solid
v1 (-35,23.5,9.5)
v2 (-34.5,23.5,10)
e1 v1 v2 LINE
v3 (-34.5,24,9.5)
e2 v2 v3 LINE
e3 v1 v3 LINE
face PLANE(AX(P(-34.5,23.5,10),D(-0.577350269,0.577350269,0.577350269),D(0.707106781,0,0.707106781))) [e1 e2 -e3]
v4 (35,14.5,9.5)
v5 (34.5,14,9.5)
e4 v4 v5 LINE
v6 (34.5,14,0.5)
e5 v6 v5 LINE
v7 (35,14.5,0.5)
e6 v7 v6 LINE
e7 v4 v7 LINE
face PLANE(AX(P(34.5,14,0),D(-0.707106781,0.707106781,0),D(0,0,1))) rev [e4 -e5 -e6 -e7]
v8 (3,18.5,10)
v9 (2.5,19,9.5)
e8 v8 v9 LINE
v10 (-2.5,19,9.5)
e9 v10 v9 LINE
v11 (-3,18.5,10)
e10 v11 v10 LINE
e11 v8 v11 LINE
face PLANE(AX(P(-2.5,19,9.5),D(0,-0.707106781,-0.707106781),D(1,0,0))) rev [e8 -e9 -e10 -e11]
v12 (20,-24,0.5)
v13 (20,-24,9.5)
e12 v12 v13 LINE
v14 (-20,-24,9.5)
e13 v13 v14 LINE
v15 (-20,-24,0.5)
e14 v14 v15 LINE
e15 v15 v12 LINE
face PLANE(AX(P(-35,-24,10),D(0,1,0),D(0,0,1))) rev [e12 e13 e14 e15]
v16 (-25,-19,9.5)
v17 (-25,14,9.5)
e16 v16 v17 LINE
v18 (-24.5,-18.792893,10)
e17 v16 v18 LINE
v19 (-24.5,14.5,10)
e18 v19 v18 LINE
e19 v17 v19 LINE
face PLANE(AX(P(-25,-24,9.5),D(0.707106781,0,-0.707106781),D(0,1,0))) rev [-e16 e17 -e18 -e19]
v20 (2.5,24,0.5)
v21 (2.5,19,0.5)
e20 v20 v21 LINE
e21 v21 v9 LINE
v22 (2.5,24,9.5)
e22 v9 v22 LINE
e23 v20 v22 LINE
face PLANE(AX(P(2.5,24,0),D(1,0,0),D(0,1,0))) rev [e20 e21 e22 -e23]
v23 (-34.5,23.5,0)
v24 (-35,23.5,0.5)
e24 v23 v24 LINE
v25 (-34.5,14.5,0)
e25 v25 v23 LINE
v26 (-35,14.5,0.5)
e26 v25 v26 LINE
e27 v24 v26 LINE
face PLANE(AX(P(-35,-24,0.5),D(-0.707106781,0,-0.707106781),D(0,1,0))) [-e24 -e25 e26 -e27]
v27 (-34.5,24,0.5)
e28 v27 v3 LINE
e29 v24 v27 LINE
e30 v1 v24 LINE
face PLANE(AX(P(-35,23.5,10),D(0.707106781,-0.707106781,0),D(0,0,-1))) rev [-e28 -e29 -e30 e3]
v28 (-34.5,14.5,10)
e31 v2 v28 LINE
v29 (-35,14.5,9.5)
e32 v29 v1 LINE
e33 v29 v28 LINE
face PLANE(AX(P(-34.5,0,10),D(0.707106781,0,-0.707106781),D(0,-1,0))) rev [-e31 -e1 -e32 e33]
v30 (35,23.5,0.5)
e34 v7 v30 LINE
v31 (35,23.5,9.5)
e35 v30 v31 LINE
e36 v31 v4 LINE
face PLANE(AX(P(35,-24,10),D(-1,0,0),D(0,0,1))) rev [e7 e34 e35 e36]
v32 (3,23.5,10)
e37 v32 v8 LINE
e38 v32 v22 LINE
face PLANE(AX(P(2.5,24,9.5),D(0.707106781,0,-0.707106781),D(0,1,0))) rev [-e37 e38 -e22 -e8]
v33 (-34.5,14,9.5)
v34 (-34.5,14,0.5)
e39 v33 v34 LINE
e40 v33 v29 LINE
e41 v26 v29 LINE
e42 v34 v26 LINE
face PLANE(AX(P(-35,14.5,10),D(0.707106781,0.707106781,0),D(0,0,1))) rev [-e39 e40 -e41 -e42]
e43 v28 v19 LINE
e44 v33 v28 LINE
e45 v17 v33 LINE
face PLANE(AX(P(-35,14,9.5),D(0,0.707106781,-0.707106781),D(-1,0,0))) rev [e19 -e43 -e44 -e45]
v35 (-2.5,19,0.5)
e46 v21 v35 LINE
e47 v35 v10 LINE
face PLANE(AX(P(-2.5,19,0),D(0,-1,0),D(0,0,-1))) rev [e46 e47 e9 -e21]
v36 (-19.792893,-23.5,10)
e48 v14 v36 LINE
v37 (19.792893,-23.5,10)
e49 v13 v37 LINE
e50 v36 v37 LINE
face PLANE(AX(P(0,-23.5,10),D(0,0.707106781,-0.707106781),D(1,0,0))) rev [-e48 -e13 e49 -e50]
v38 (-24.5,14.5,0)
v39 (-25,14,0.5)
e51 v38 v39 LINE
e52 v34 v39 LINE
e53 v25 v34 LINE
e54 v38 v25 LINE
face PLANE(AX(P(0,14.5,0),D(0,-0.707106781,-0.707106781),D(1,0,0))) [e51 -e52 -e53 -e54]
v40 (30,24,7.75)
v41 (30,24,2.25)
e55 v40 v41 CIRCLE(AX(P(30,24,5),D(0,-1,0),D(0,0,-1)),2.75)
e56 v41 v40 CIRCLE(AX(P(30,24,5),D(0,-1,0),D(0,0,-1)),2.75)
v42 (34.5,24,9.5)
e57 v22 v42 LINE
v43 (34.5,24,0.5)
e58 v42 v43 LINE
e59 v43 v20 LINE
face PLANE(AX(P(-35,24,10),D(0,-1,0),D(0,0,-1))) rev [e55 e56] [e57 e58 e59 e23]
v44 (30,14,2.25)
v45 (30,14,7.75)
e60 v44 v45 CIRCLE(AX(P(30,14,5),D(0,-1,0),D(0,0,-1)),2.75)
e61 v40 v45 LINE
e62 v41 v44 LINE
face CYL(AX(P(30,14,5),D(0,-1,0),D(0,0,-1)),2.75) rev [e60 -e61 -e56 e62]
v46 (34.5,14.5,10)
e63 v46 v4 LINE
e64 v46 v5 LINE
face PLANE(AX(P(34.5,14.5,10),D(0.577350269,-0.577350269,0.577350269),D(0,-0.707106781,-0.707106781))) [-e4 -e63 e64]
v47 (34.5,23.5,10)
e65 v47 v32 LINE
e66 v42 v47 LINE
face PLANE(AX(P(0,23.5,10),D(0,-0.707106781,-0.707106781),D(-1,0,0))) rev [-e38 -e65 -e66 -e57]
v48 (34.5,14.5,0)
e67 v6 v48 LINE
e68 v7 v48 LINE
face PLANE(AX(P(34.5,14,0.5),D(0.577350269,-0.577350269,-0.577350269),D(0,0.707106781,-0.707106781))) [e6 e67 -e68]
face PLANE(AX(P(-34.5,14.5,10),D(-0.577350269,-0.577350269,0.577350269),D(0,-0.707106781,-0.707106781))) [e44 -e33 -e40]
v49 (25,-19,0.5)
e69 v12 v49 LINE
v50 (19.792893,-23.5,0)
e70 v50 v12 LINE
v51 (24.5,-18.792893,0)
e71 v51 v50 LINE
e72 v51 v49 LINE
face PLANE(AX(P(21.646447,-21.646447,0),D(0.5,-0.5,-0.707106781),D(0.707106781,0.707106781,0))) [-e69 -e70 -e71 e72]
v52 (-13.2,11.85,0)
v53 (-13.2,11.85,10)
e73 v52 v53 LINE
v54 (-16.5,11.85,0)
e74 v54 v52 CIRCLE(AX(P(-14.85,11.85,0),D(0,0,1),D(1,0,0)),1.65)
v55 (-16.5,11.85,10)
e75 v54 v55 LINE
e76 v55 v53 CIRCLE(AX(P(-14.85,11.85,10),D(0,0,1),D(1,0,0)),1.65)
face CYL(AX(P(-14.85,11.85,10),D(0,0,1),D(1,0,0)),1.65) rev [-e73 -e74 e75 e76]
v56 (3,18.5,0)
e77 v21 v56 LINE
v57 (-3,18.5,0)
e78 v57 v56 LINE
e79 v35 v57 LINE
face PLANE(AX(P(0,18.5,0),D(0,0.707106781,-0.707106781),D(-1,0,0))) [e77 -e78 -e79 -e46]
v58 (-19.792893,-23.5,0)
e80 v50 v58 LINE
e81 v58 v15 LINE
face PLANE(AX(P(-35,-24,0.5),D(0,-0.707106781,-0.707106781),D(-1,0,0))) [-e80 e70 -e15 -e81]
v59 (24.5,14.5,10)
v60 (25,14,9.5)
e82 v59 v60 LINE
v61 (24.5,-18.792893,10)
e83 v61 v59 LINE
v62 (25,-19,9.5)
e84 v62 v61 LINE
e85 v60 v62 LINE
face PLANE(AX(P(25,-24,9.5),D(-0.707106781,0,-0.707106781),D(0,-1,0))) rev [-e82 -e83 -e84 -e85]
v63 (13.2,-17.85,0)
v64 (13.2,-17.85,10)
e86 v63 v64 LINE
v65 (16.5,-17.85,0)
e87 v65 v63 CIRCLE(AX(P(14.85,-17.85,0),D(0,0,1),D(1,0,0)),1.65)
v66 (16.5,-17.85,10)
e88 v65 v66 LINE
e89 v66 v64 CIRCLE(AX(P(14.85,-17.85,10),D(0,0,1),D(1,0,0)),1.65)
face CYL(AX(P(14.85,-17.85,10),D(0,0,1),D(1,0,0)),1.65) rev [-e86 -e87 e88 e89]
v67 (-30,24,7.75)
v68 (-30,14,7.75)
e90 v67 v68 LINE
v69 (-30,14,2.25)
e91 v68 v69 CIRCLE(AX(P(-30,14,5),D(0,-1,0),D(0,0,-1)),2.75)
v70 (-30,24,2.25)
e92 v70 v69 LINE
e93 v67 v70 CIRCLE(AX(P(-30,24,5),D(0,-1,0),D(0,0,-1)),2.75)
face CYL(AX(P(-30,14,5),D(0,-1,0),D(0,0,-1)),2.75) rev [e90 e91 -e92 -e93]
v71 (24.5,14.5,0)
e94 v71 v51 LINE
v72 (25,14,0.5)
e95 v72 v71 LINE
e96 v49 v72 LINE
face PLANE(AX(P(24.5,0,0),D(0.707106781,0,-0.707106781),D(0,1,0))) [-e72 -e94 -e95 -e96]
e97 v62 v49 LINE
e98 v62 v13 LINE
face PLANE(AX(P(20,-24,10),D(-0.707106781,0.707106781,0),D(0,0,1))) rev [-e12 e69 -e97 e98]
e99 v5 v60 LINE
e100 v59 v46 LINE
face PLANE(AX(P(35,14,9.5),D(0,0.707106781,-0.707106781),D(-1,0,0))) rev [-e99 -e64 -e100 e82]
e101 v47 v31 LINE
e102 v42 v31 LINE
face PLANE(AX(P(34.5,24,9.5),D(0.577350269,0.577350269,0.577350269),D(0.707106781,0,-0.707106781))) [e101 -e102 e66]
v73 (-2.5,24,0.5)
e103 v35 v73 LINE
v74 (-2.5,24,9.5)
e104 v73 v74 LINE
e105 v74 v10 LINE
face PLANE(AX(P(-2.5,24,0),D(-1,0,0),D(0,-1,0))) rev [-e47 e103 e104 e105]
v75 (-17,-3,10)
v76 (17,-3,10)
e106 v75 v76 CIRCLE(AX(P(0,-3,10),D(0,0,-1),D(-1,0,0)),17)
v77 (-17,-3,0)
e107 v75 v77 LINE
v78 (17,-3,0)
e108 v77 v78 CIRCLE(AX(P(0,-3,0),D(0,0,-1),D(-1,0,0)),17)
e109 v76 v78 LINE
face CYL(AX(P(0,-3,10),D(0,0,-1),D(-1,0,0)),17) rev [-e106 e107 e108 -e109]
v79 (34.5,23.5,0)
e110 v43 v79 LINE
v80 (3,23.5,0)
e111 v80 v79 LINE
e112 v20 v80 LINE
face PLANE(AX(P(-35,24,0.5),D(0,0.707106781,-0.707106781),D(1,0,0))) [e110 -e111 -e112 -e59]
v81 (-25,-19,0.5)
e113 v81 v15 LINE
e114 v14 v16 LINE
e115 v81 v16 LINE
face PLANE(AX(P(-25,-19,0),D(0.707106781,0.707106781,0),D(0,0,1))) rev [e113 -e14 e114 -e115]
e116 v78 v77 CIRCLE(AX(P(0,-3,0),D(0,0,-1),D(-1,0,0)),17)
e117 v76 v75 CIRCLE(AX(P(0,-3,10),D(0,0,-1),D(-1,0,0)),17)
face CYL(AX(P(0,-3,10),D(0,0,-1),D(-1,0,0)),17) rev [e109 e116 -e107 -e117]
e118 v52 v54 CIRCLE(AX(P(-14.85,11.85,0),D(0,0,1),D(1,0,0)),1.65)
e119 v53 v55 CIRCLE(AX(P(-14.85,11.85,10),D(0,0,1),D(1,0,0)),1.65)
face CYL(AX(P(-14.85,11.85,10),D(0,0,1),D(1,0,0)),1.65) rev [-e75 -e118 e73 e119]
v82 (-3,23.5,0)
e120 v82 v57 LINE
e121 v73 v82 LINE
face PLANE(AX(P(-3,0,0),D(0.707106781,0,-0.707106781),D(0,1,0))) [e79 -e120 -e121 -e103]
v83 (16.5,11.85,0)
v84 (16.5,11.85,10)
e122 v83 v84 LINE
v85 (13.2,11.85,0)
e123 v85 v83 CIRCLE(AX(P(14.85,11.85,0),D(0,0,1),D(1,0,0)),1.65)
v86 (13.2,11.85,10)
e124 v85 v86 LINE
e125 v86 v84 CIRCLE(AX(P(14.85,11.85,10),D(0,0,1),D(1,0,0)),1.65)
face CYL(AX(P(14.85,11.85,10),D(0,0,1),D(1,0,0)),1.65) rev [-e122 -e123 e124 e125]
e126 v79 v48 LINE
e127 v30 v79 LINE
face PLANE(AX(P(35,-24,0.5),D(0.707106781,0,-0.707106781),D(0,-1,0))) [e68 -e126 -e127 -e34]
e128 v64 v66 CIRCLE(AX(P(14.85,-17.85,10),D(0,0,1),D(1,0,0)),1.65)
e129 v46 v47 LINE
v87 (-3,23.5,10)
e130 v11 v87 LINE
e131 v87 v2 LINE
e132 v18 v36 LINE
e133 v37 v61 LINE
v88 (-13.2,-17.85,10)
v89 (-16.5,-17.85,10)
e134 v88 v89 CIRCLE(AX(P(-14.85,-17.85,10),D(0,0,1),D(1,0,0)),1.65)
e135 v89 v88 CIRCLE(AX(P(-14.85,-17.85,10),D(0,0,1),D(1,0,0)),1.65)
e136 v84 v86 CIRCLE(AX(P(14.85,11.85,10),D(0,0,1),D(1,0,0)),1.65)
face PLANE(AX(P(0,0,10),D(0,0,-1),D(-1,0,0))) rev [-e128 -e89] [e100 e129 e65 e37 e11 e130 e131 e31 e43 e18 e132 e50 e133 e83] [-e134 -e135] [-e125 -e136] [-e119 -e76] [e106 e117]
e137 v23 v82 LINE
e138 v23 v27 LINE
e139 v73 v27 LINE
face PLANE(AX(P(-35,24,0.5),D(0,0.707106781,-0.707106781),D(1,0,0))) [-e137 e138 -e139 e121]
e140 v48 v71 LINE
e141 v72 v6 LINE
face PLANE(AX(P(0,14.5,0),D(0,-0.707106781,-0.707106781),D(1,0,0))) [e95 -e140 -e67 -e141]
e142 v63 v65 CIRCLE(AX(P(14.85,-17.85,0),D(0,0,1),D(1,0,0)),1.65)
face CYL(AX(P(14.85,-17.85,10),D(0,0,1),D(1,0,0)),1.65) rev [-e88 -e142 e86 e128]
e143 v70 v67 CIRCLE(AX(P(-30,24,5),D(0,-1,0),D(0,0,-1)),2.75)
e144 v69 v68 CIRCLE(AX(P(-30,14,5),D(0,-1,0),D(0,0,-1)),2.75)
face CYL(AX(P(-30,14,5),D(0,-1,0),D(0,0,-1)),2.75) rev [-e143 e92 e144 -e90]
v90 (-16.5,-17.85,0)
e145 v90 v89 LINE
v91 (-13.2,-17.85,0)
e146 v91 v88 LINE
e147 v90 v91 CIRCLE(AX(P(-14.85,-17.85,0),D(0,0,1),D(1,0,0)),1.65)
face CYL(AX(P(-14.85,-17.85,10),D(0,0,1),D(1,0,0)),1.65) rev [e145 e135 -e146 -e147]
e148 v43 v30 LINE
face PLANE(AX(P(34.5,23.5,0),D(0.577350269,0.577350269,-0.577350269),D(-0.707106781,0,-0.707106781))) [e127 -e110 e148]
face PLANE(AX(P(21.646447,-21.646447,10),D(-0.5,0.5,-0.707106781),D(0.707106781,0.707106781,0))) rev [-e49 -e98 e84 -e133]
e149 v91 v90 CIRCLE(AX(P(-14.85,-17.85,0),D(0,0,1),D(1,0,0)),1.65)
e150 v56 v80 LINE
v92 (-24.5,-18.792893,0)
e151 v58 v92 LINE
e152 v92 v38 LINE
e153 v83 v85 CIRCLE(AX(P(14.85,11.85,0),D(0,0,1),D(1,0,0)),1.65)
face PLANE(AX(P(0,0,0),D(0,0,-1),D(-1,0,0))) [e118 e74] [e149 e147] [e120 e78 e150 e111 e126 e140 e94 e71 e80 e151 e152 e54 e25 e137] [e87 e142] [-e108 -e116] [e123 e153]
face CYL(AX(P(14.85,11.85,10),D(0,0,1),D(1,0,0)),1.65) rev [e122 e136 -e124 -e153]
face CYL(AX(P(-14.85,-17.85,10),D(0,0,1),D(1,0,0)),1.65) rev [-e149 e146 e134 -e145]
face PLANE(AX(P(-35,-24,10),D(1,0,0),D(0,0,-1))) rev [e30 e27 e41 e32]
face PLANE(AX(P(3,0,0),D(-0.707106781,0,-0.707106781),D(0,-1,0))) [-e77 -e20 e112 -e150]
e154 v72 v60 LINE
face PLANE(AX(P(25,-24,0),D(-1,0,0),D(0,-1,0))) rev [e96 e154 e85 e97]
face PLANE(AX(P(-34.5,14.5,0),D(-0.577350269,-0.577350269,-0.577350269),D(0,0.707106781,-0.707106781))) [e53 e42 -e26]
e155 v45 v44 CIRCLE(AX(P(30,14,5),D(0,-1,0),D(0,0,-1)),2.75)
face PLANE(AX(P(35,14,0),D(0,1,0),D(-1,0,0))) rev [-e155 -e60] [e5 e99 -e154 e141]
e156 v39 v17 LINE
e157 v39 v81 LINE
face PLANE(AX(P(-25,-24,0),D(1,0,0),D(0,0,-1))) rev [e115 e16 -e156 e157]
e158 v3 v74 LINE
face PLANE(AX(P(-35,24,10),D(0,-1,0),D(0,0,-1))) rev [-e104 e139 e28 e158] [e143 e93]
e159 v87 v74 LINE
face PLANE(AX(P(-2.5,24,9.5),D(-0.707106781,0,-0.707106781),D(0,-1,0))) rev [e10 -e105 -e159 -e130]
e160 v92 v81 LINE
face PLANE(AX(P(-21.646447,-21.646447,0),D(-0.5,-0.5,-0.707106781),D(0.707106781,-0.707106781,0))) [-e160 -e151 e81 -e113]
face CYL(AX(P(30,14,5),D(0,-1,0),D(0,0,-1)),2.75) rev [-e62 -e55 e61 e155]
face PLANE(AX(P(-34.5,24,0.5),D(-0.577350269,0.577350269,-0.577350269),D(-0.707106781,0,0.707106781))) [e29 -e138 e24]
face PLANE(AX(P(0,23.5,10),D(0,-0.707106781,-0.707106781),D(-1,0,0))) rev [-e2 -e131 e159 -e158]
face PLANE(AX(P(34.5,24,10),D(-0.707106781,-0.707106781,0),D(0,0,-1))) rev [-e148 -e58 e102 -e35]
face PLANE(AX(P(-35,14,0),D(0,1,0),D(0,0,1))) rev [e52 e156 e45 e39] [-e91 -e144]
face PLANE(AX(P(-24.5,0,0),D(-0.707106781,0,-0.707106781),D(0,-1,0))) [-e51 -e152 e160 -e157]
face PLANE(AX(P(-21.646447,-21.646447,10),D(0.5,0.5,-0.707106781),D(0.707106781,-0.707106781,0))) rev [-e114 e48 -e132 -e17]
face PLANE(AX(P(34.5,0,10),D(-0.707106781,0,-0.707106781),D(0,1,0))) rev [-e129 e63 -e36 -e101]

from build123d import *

# Parameters (mm, degrees)
SKETCH_1_W              = 70
SKETCH_1_H              = 48
EXTRUDE_1_DEPTH         = 10
SKETCH_2_W              = 10
SKETCH_2_H              = 38
CUT_EXTRUDE_1_DEPTH     = 44.600458713
SKETCH_3_R              = 17
CUT_EXTRUDE_2_DEPTH     = 44.600458713
HOLE_WIZARD_M4_2_D      = 3.3
HOLE_WIZARD_5_5_5_5_1_D = 5.5
CHAMFER_1_SIZE          = 5
SKETCH_12_W             = 5
SKETCH_12_H             = 5
CUT_EXTRUDE_3_DEPTH     = 44.600458713
CHAMFER_2_SIZE          = 0.5


with BuildPart() as part:
    # 草图1 → 凸台-拉伸1 (new body)
    with BuildSketch(Plane.XY):
        Rectangle(SKETCH_1_W, SKETCH_1_H)
    extrude(amount=EXTRUDE_1_DEPTH)

    # 草图2 → 切除-拉伸1 (cut, through all)
    with BuildSketch(Plane.XY.offset(10)):
        with Locations((-30, -5)):
            Rectangle(SKETCH_2_W, SKETCH_2_H)
        with Locations((30, -5)):
            Rectangle(SKETCH_2_W, SKETCH_2_H)
    extrude(amount=-CUT_EXTRUDE_1_DEPTH, mode=Mode.SUBTRACT)

    # 草图3 → 切除-拉伸2 (cut, through all)
    with BuildSketch(Plane(origin=(0, 0, 0), x_dir=(-1, 0, 0), z_dir=(0, 0, -1))):
        with Locations((0, -3)):
            Circle(SKETCH_3_R)
    extrude(amount=-CUT_EXTRUDE_2_DEPTH, mode=Mode.SUBTRACT)

    # M4 螺纹孔2 (through all)
    with Locations(Plane.XY.offset(10)):
        with Locations((14.85, -17.85), (-14.85, -17.85), (-14.85, 11.85), (14.85, 11.85)):
            Hole(HOLE_WIZARD_M4_2_D / 2)

    # Ø5.5 (5.5) 直径孔1 (through all)
    with Locations(Plane(origin=(0, 14, 0), x_dir=(-1, 0, 0), z_dir=(0, -1, 0))):
        with Locations((-30, -5), (30, -5)):
            Hole(HOLE_WIZARD_5_5_5_5_1_D / 2)

    # 倒角1
    chamfer_1_edges = [part.edges().sort_by_distance(p)[0] for p in [
        (-25, -24, 5),
        (25, -24, 5),
    ]]
    chamfer(chamfer_1_edges, length=CHAMFER_1_SIZE)

    # 草图12 → 切除-拉伸3 (cut, through all)
    with BuildSketch(Plane.XY.offset(10)):
        with Locations((0, 21.5)):
            Rectangle(SKETCH_12_W, SKETCH_12_H)
    extrude(amount=-CUT_EXTRUDE_3_DEPTH, mode=Mode.SUBTRACT)

    # 倒角2
    chamfer_2_edges = [part.edges().sort_by_distance(p)[0] for p in [
        (-35, 19, 10),
        (-30, 14, 0),
        (-35, 14, 5),
        (-30, 14, 10),
        (35, 19, 0),
        (35, 19, 10),
        (25, -2.5, 0),
        (30, 14, 0),
        (35, 14, 5),
        (30, 14, 10),
        (25, -2.5, 10),
        (-35, 19, 0),
        (18.75, 24, 0),
        (18.75, 24, 10),
        (-35, 24, 5),
        (35, 24, 5),
        (-25, -2.5, 10),
        (-25, -2.5, 0),
        (0, -24, 10),
        (22.5, -21.5, 10),
        (-22.5, -21.5, 10),
        (0, -24, 0),
        (22.5, -21.5, 0),
        (-22.5, -21.5, 0),
        (-18.75, 24, 0),
        (-18.75, 24, 10),
        (-2.5, 21.5, 0),
        (2.5, 21.5, 0),
        (0, 19, 0),
        (-2.5, 21.5, 10),
        (0, 19, 10),
        (2.5, 21.5, 10),
    ]]
    chamfer(chamfer_2_edges, length=CHAMFER_2_SIZE)


solid = part.part
